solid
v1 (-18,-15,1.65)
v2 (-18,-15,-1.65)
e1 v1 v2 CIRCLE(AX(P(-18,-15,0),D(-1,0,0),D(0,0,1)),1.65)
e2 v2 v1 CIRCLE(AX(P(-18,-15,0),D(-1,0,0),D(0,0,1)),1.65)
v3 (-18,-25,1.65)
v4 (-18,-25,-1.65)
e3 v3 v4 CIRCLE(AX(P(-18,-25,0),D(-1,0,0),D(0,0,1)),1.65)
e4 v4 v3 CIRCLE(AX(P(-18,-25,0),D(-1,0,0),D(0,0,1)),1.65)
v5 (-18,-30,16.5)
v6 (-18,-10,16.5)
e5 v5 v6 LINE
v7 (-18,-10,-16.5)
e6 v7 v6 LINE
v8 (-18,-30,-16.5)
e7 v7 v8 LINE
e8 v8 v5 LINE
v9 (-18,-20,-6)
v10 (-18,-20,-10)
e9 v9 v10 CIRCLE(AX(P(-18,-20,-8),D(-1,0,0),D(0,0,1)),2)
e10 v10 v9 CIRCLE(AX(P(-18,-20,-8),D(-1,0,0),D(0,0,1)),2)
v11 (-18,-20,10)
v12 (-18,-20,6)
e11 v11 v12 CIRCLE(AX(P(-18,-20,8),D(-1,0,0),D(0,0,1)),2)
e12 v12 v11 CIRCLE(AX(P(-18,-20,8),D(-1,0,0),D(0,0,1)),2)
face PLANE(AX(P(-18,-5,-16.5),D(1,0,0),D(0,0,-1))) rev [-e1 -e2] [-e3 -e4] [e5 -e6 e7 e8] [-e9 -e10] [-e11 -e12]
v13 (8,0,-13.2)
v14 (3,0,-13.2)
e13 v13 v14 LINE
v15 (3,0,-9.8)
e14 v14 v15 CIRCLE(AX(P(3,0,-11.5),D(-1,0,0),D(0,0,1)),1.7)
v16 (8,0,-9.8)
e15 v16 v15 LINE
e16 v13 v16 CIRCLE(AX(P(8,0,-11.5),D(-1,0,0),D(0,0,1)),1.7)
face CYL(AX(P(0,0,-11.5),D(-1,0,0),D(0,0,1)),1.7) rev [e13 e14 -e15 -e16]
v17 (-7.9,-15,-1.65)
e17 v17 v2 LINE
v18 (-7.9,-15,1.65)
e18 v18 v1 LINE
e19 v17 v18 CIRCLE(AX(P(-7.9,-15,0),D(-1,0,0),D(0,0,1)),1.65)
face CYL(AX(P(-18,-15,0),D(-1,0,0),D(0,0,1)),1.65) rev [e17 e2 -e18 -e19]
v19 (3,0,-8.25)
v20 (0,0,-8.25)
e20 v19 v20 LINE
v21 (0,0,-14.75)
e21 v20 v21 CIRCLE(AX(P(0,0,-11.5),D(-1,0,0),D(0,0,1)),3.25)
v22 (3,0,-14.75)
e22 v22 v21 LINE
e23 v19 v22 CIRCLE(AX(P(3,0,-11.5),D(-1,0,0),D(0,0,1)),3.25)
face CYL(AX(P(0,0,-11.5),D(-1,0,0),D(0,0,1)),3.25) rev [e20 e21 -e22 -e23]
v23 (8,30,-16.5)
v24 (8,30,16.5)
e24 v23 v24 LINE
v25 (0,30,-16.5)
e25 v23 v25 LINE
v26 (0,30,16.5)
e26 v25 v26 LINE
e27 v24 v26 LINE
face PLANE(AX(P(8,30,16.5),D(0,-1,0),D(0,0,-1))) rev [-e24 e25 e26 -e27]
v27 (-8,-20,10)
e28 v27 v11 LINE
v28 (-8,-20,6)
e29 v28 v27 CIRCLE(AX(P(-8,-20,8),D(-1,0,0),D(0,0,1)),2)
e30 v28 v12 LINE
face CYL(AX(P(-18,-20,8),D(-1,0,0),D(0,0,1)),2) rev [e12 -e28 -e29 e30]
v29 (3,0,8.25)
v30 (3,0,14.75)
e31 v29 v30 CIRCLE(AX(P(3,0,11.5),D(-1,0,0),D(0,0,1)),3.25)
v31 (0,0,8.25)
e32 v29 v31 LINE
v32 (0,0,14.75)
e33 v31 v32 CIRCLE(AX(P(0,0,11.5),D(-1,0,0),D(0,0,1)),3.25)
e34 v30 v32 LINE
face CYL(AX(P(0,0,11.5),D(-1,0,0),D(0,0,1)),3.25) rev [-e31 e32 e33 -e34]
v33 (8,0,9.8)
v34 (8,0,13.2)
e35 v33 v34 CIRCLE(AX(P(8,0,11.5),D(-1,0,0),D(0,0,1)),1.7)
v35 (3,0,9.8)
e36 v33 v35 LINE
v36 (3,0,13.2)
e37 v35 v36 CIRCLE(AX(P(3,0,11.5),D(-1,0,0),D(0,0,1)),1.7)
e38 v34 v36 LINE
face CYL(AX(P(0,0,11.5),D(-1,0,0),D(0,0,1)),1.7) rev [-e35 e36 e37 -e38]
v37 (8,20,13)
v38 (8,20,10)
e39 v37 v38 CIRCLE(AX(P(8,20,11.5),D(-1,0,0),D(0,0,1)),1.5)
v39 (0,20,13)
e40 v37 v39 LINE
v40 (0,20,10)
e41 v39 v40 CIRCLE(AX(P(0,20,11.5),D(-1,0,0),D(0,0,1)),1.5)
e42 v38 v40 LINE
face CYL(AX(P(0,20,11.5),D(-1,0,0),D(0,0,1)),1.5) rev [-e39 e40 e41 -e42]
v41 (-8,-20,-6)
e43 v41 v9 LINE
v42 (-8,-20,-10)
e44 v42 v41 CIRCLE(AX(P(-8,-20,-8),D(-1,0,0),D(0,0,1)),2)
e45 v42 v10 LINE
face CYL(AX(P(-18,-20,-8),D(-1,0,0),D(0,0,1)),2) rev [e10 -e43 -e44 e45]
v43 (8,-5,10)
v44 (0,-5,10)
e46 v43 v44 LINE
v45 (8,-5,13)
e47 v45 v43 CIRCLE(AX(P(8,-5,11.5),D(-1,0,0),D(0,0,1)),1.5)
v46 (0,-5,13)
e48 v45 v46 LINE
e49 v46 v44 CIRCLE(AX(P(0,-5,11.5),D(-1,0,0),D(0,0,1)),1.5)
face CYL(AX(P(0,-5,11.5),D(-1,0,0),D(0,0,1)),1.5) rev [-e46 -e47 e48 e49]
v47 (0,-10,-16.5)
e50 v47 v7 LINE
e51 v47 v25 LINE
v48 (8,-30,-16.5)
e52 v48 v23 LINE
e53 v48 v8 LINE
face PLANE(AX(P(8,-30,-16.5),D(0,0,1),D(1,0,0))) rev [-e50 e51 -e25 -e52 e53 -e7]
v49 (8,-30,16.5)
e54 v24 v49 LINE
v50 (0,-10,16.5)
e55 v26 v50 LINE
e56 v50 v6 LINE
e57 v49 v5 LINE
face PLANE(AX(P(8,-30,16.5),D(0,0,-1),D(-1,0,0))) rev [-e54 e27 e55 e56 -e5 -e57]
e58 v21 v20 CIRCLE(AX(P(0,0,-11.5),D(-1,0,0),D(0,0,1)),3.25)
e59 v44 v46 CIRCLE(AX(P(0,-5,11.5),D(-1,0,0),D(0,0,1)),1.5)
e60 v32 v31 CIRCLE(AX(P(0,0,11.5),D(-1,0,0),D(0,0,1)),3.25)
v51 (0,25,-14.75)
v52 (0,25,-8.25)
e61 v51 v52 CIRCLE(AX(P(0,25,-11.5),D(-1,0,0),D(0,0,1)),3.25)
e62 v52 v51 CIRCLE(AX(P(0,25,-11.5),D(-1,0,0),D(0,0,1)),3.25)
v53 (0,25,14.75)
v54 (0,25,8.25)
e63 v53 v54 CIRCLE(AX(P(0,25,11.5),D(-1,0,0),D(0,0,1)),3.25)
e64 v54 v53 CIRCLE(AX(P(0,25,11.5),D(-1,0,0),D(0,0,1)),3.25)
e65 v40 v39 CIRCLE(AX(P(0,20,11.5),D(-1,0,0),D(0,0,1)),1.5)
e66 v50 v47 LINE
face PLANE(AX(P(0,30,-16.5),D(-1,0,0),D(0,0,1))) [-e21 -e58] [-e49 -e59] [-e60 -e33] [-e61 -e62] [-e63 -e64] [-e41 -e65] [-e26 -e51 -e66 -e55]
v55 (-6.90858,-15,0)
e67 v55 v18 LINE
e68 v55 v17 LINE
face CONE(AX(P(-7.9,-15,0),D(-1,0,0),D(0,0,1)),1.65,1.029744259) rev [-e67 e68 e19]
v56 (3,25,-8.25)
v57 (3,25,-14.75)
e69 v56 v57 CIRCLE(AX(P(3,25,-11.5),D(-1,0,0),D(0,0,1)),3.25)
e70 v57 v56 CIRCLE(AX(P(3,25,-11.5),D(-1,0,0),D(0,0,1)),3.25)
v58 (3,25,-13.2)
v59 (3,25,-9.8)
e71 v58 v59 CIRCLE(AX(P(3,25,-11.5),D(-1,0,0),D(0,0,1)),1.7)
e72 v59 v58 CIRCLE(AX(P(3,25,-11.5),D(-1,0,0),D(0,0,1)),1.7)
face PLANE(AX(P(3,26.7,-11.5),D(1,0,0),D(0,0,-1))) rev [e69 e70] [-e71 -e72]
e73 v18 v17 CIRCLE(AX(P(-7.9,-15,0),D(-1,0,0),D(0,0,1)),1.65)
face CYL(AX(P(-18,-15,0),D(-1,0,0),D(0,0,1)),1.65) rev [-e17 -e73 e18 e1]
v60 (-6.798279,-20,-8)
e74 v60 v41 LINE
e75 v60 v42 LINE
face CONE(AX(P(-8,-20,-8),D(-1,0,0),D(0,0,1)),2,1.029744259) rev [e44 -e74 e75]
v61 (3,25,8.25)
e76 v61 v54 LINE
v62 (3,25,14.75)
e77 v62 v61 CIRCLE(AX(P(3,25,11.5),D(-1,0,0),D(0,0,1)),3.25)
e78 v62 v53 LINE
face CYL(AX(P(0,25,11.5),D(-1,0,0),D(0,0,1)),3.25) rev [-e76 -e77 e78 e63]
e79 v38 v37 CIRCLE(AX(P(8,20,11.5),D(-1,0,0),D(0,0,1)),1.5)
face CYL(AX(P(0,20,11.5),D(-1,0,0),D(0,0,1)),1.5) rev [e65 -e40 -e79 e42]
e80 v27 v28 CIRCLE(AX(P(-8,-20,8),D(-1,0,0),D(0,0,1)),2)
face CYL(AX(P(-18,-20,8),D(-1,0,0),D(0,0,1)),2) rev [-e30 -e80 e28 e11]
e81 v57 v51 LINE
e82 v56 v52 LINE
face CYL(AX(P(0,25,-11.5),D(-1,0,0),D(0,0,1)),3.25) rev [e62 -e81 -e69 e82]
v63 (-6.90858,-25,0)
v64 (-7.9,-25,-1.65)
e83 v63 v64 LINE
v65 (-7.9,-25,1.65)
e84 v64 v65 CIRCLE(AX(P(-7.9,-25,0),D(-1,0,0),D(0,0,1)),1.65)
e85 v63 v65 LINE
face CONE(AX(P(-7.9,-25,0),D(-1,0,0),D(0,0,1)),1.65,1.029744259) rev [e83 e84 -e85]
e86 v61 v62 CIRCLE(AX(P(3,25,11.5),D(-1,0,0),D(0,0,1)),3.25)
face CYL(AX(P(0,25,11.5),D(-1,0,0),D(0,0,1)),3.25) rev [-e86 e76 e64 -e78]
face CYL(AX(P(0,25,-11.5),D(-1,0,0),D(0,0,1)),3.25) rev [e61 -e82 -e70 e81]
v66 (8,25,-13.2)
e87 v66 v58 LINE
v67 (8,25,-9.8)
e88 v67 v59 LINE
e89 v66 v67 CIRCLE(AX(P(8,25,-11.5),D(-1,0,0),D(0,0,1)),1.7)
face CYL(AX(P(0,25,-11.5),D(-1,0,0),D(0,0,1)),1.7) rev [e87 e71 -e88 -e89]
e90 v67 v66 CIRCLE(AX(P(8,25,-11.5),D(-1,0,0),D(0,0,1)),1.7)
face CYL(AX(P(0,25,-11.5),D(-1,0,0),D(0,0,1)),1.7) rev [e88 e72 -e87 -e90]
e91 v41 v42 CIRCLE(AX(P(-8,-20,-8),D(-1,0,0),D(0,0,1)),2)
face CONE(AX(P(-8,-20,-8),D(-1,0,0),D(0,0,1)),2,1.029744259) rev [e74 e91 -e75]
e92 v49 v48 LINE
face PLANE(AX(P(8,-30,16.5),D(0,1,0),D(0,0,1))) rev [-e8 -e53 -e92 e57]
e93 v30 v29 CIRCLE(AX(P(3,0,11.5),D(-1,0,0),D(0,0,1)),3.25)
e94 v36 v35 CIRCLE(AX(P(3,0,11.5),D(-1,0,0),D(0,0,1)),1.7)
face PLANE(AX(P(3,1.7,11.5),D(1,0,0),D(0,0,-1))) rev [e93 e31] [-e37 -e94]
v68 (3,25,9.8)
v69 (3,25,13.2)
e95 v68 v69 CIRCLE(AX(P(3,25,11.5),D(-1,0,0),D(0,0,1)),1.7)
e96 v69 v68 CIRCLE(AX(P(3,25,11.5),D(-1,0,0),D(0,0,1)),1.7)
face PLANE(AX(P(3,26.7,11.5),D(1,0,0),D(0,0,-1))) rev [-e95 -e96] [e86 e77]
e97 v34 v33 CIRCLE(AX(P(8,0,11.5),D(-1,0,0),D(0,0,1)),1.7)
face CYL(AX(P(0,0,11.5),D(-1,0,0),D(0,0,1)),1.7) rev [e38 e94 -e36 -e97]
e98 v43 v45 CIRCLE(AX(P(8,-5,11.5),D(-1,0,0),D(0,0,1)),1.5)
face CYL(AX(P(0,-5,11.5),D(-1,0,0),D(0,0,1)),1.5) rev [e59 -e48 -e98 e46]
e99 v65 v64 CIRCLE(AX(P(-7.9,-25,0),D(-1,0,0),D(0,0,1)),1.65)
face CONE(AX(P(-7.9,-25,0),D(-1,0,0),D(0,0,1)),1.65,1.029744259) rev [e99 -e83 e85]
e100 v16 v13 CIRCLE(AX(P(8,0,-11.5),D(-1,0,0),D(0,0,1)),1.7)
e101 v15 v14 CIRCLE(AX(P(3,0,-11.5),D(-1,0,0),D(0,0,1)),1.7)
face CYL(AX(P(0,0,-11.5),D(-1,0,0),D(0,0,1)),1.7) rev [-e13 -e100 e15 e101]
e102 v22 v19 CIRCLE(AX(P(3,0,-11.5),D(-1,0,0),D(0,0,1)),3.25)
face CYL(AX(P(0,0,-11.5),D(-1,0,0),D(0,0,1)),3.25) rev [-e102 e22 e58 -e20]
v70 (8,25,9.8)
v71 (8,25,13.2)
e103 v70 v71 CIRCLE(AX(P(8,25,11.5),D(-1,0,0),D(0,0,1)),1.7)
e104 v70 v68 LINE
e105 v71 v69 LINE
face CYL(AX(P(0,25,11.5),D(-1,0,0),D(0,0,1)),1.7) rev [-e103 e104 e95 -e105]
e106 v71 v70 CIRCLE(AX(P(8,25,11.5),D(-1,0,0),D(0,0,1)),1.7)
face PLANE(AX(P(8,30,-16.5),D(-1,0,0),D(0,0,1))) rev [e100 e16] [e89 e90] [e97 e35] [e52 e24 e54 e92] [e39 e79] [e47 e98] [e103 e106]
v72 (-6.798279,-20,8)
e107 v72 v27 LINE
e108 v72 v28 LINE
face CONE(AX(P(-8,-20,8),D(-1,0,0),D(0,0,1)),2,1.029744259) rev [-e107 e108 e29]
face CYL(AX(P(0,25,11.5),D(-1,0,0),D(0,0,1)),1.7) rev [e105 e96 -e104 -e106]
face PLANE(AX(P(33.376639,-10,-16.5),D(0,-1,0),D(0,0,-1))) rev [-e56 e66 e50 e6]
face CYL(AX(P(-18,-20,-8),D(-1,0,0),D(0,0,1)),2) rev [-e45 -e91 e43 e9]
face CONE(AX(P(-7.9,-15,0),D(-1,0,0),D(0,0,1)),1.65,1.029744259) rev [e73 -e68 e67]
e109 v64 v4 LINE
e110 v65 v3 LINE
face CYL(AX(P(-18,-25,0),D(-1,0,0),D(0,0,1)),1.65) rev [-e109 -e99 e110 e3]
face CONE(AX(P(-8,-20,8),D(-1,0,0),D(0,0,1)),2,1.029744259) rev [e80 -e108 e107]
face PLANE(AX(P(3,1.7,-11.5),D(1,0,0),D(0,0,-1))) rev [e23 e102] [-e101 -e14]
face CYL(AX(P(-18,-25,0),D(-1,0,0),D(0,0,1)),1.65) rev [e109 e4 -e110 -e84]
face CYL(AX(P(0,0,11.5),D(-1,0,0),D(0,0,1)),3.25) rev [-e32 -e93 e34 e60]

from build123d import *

# Parameters (mm, degrees)
SKETCH_1_W                                        = 33
SKETCH_1_H                                        = 60
BOSS_EXTRUDE_1_DEPTH                              = 8
SKETCH_2_W                                        = 33
SKETCH_2_H                                        = 25
BOSS_EXTRUDE_2_DEPTH                              = 18
M3_HEX_SOCKET_CAP_SCREW_COUNTERBORE_1_D           = 3.4
M3_HEX_SOCKET_CAP_SCREW_COUNTERBORE_1_CBORE_D     = 6.5
M3_HEX_SOCKET_CAP_SCREW_COUNTERBORE_1_CBORE_DEPTH = 3
LINEAR_PATTERN_1_COUNT                            = 2
LINEAR_PATTERN_1_PITCH                            = 23
LINEAR_PATTERN_1_COUNT_DIR2                       = 2
LINEAR_PATTERN_1_PITCH_DIR2                       = 25
LINEAR_PATTERN_2_COUNT                            = 2
LINEAR_PATTERN_2_PITCH                            = 10
SKETCH_9_W                                        = 33
SKETCH_9_H                                        = 5
CUT_EXTRUDE_1_DEPTH                               = 18
F_3_0_3_HOLE_1_D                                  = 3
LINEAR_PATTERN_3_COUNT                            = 2
LINEAR_PATTERN_3_PITCH                            = 25
LINEAR_PATTERN_4_COUNT                            = 2
LINEAR_PATTERN_4_PITCH                            = 16


with BuildPart() as part:
    # Sketch 1 → Boss-Extrude 1 (new body)
    with BuildSketch(Plane(origin=(0, 0, 0), x_dir=(0, 0, -1), z_dir=(1, 0, 0))):
        Rectangle(SKETCH_1_W, SKETCH_1_H)
    extrude(amount=BOSS_EXTRUDE_1_DEPTH)

    # Sketch 2 → Boss-Extrude 2 (add)
    with BuildSketch(Plane.ZY):
        with Locations((0, -17.5)):
            Rectangle(SKETCH_2_W, SKETCH_2_H)
    extrude(amount=BOSS_EXTRUDE_2_DEPTH)

    # M3 Hex Socket Cap Screw Counterbore 1 (through all)
    with Locations(Plane.ZY):
        with Locations((-11.5, 25)):
            m3_hex_socket_cap_screw_counterbore_1 = CounterBoreHole(M3_HEX_SOCKET_CAP_SCREW_COUNTERBORE_1_D / 2, M3_HEX_SOCKET_CAP_SCREW_COUNTERBORE_1_CBORE_D / 2, M3_HEX_SOCKET_CAP_SCREW_COUNTERBORE_1_CBORE_DEPTH)

    # Linear Pattern 1: M3 Hex Socket Cap Screw Counterbore 1 2 × 2
    with Locations(*[(0, -j * LINEAR_PATTERN_1_PITCH_DIR2, i * LINEAR_PATTERN_1_PITCH) for i in range(LINEAR_PATTERN_1_COUNT) for j in range(LINEAR_PATTERN_1_COUNT_DIR2) if (i, j) != (0, 0)]):
        add(m3_hex_socket_cap_screw_counterbore_1, mode=Mode.SUBTRACT)

    # Sketch 7 → M4 Tapped Hole 2 (revolve, cut)
    with BuildSketch(Plane(origin=(-18, -25, 0), x_dir=(0, 0, 1), z_dir=(0, 1, 0))):
        Polygon((0, 0), (0, 11.091420021), (1.65, 10.1), (1.65, 0), align=None)
    m4_tapped_hole_2 = revolve(axis=Axis((-24.35, -25, 0), (1, 0, 0)), mode=Mode.SUBTRACT)

    # Linear Pattern 2: M4 Tapped Hole 2 ×2
    with Locations(*[(0, i * LINEAR_PATTERN_2_PITCH, 0) for i in range(1, LINEAR_PATTERN_2_COUNT)]):
        add(m4_tapped_hole_2, mode=Mode.SUBTRACT)

    # Sketch 9 → Cut-Extrude 1 (cut)
    with BuildSketch(Plane.ZY.offset(18)):
        with Locations((0, -7.5)):
            Rectangle(SKETCH_9_W, SKETCH_9_H)
    extrude(amount=-CUT_EXTRUDE_1_DEPTH, mode=Mode.SUBTRACT)

    # Ø3.0 (3) Hole 1 (through all)
    with Locations(Plane.ZY):
        with Locations((11.5, 20)):
            f_3_0_3_hole_1 = Hole(F_3_0_3_HOLE_1_D / 2)

    # Linear Pattern 3: Ø3.0 (3) Hole 1 ×2
    with Locations(*[(0, -i * LINEAR_PATTERN_3_PITCH, 0) for i in range(1, LINEAR_PATTERN_3_COUNT)]):
        add(f_3_0_3_hole_1, mode=Mode.SUBTRACT)

    # Sketch 12 → Ø4.0 (4) Hole 1 (revolve, cut)
    with BuildSketch(Plane(origin=(-18, -20, -8), x_dir=(0, 0, 1), z_dir=(0, 1, 0))):
        Polygon((0, 0), (0, 11.201721238), (2, 10), (2, 0), align=None)
    f_4_0_4_hole_1 = revolve(axis=Axis((-24.35, -20, -8), (1, 0, 0)), mode=Mode.SUBTRACT)

    # Linear Pattern 4: Ø4.0 (4) Hole 1 ×2
    with Locations(*[(0, 0, i * LINEAR_PATTERN_4_PITCH) for i in range(1, LINEAR_PATTERN_4_COUNT)]):
        add(f_4_0_4_hole_1, mode=Mode.SUBTRACT)


solid = part.part
